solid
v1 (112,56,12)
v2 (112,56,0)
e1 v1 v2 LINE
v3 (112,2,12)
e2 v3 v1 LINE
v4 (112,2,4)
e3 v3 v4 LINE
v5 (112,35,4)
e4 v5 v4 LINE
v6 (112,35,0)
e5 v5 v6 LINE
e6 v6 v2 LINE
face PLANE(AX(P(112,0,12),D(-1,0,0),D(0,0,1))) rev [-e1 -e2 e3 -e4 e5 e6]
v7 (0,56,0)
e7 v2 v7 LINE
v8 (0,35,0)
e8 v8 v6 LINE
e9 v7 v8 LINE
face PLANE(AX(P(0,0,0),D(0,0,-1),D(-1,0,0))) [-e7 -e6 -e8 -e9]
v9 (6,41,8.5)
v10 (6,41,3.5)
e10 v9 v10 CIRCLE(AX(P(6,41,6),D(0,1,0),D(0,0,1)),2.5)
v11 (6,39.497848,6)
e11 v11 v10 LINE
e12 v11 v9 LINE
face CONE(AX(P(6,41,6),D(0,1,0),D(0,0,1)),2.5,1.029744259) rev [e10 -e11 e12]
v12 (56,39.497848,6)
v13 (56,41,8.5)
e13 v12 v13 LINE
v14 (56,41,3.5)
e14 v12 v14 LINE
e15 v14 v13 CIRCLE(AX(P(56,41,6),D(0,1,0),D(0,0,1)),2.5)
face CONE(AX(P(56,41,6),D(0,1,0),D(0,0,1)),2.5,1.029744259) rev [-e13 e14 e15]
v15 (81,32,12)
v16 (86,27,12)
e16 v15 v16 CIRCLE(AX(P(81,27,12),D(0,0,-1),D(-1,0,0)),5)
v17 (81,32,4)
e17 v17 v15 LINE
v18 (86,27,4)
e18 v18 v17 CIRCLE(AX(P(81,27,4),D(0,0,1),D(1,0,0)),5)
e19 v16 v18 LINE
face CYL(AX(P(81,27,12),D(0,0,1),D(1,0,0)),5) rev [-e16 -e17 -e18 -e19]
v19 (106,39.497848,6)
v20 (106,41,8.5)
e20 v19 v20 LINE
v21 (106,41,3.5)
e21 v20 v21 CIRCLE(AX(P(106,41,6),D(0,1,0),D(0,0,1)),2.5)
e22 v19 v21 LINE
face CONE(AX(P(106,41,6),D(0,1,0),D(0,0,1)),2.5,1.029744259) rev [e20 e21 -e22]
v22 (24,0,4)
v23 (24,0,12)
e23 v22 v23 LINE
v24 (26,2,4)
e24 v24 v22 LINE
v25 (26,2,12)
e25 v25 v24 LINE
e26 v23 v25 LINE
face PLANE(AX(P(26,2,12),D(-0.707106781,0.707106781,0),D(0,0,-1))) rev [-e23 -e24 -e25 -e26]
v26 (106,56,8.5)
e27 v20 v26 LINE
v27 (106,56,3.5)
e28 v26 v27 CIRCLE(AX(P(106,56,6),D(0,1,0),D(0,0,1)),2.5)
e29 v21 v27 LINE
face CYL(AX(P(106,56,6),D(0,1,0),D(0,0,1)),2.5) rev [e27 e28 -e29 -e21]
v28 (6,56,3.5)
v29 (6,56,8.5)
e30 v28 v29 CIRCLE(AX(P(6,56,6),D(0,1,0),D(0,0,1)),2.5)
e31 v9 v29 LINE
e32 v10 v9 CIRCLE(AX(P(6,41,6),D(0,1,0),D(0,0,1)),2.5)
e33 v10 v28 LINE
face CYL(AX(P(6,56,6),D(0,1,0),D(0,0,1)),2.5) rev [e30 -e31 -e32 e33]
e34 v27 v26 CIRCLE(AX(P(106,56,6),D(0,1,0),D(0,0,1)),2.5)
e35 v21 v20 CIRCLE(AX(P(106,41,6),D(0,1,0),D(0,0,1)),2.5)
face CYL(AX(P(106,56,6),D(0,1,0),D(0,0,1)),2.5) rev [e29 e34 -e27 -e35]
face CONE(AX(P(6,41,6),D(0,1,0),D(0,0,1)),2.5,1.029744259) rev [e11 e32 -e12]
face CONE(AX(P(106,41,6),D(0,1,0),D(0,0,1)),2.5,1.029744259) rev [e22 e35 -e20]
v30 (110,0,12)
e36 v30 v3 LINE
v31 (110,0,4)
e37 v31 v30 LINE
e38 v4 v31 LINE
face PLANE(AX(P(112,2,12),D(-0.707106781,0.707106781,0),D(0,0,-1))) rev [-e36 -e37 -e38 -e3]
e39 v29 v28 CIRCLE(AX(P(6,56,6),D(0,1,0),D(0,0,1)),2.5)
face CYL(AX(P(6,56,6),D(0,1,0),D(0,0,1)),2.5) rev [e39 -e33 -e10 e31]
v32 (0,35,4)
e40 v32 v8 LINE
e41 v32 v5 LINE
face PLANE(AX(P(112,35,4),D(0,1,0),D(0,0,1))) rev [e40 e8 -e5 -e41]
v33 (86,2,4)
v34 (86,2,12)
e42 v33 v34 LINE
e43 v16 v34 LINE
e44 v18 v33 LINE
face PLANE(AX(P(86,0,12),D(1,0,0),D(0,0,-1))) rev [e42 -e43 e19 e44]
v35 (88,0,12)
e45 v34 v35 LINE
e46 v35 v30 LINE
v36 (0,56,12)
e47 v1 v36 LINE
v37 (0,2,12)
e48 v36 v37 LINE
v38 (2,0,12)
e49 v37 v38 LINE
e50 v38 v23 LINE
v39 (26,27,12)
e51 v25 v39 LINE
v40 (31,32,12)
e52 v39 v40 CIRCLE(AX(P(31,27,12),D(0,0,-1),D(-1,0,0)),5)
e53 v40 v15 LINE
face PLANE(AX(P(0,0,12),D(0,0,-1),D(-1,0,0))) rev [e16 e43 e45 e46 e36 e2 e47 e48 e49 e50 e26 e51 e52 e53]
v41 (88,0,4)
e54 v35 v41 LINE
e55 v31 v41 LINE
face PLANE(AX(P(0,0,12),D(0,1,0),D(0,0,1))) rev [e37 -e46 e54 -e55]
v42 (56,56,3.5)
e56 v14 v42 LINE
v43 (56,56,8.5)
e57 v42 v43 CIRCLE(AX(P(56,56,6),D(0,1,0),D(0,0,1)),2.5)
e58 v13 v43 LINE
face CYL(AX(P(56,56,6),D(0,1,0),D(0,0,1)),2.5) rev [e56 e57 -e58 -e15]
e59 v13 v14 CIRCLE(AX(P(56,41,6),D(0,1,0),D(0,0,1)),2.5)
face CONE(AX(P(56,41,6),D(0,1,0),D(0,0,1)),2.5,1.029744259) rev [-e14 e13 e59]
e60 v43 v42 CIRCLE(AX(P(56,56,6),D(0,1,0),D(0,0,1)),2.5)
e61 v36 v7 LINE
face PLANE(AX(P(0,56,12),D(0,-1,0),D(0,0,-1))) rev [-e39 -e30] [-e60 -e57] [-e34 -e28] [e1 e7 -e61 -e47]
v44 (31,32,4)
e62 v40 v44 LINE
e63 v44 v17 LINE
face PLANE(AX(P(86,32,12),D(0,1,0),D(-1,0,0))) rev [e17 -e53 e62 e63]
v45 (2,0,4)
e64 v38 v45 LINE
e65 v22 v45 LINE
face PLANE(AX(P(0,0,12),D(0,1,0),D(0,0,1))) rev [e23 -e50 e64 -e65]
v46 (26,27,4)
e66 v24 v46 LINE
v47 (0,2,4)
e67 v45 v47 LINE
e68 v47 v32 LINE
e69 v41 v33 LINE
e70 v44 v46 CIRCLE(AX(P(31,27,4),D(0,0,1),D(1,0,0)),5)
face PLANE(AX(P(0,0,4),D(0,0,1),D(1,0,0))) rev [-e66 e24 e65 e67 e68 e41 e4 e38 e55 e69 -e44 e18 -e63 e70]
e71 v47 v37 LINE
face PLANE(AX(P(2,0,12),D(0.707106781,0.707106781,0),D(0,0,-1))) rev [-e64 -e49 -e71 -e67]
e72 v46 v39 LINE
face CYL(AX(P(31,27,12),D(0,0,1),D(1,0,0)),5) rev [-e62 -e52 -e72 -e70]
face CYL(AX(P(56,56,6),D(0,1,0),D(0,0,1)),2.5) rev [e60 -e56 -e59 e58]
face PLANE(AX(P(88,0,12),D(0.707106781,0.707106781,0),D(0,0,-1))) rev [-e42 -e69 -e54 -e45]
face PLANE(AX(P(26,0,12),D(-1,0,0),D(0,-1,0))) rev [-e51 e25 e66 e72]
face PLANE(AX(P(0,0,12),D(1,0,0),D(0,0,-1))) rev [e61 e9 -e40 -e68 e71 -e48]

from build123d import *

# Parameters (mm, degrees)
SKETCH1_W             = 112
SKETCH1_H             = 56
BOSS_EXTRUDE1_DEPTH   = 12
SKETCH2_W             = 112
SKETCH2_H             = 35
CUT_EXTRUDE1_DEPTH    = 4
M6_TAPPED_HOLE1_D     = 5
M6_TAPPED_HOLE1_DEPTH = 15
M6_TAPPED_HOLE1_TIP   = 1.502151548
SKETCH6_W             = 60
SKETCH6_H             = 32
CUT_EXTRUDE2_DEPTH    = 126.475097131
FILLET1_R             = 5
CHAMFER1_SIZE         = 2


with BuildPart() as part:
    # Sketch1 → Boss-Extrude1 (new body)
    with BuildSketch(Plane.XY):
        with Locations((56, 28)):
            Rectangle(SKETCH1_W, SKETCH1_H)
    extrude(amount=BOSS_EXTRUDE1_DEPTH)

    # Sketch2 → Cut-Extrude1 (cut)
    with BuildSketch(Plane(origin=(0, 0, 0), x_dir=(-1, 0, 0), z_dir=(0, 0, -1))):
        with Locations((-56, 17.5)):
            Rectangle(SKETCH2_W, SKETCH2_H)
    extrude(amount=-CUT_EXTRUDE1_DEPTH, mode=Mode.SUBTRACT)

    # M6 Tapped Hole1
    with Locations(Plane(origin=(0, 56, 0), x_dir=(1, 0, 0), z_dir=(0, 1, 0))):
        with Locations((106, -6), (6, -6), (56, -6)):
            Hole(M6_TAPPED_HOLE1_D / 2, depth=M6_TAPPED_HOLE1_DEPTH)
            with Locations((0, 0, -(M6_TAPPED_HOLE1_DEPTH + M6_TAPPED_HOLE1_TIP / 2))):  # 118° drill point
                Cone(0, M6_TAPPED_HOLE1_D / 2, M6_TAPPED_HOLE1_TIP, mode=Mode.SUBTRACT)

    # Sketch6 → Cut-Extrude2 (cut, through all)
    with BuildSketch(Plane(origin=(0, 0, 4), x_dir=(-1, 0, 0), z_dir=(0, 0, -1))):
        with Locations((-56, 16)):
            Rectangle(SKETCH6_W, SKETCH6_H)
    extrude(amount=-CUT_EXTRUDE2_DEPTH, mode=Mode.SUBTRACT)

    # Fillet1
    fillet1_edges = [part.edges().sort_by_distance(p)[0] for p in [
        (86, 32, 8),
        (26, 32, 8),
    ]]
    fillet(fillet1_edges, radius=FILLET1_R)

    # Chamfer1
    chamfer1_edges = [part.edges().sort_by_distance(p)[0] for p in [
        (86, 0, 8),
        (26, 0, 8),
        (112, 0, 8),
        (0, 0, 8),
    ]]
    chamfer(chamfer1_edges, length=CHAMFER1_SIZE)


solid = part.part
